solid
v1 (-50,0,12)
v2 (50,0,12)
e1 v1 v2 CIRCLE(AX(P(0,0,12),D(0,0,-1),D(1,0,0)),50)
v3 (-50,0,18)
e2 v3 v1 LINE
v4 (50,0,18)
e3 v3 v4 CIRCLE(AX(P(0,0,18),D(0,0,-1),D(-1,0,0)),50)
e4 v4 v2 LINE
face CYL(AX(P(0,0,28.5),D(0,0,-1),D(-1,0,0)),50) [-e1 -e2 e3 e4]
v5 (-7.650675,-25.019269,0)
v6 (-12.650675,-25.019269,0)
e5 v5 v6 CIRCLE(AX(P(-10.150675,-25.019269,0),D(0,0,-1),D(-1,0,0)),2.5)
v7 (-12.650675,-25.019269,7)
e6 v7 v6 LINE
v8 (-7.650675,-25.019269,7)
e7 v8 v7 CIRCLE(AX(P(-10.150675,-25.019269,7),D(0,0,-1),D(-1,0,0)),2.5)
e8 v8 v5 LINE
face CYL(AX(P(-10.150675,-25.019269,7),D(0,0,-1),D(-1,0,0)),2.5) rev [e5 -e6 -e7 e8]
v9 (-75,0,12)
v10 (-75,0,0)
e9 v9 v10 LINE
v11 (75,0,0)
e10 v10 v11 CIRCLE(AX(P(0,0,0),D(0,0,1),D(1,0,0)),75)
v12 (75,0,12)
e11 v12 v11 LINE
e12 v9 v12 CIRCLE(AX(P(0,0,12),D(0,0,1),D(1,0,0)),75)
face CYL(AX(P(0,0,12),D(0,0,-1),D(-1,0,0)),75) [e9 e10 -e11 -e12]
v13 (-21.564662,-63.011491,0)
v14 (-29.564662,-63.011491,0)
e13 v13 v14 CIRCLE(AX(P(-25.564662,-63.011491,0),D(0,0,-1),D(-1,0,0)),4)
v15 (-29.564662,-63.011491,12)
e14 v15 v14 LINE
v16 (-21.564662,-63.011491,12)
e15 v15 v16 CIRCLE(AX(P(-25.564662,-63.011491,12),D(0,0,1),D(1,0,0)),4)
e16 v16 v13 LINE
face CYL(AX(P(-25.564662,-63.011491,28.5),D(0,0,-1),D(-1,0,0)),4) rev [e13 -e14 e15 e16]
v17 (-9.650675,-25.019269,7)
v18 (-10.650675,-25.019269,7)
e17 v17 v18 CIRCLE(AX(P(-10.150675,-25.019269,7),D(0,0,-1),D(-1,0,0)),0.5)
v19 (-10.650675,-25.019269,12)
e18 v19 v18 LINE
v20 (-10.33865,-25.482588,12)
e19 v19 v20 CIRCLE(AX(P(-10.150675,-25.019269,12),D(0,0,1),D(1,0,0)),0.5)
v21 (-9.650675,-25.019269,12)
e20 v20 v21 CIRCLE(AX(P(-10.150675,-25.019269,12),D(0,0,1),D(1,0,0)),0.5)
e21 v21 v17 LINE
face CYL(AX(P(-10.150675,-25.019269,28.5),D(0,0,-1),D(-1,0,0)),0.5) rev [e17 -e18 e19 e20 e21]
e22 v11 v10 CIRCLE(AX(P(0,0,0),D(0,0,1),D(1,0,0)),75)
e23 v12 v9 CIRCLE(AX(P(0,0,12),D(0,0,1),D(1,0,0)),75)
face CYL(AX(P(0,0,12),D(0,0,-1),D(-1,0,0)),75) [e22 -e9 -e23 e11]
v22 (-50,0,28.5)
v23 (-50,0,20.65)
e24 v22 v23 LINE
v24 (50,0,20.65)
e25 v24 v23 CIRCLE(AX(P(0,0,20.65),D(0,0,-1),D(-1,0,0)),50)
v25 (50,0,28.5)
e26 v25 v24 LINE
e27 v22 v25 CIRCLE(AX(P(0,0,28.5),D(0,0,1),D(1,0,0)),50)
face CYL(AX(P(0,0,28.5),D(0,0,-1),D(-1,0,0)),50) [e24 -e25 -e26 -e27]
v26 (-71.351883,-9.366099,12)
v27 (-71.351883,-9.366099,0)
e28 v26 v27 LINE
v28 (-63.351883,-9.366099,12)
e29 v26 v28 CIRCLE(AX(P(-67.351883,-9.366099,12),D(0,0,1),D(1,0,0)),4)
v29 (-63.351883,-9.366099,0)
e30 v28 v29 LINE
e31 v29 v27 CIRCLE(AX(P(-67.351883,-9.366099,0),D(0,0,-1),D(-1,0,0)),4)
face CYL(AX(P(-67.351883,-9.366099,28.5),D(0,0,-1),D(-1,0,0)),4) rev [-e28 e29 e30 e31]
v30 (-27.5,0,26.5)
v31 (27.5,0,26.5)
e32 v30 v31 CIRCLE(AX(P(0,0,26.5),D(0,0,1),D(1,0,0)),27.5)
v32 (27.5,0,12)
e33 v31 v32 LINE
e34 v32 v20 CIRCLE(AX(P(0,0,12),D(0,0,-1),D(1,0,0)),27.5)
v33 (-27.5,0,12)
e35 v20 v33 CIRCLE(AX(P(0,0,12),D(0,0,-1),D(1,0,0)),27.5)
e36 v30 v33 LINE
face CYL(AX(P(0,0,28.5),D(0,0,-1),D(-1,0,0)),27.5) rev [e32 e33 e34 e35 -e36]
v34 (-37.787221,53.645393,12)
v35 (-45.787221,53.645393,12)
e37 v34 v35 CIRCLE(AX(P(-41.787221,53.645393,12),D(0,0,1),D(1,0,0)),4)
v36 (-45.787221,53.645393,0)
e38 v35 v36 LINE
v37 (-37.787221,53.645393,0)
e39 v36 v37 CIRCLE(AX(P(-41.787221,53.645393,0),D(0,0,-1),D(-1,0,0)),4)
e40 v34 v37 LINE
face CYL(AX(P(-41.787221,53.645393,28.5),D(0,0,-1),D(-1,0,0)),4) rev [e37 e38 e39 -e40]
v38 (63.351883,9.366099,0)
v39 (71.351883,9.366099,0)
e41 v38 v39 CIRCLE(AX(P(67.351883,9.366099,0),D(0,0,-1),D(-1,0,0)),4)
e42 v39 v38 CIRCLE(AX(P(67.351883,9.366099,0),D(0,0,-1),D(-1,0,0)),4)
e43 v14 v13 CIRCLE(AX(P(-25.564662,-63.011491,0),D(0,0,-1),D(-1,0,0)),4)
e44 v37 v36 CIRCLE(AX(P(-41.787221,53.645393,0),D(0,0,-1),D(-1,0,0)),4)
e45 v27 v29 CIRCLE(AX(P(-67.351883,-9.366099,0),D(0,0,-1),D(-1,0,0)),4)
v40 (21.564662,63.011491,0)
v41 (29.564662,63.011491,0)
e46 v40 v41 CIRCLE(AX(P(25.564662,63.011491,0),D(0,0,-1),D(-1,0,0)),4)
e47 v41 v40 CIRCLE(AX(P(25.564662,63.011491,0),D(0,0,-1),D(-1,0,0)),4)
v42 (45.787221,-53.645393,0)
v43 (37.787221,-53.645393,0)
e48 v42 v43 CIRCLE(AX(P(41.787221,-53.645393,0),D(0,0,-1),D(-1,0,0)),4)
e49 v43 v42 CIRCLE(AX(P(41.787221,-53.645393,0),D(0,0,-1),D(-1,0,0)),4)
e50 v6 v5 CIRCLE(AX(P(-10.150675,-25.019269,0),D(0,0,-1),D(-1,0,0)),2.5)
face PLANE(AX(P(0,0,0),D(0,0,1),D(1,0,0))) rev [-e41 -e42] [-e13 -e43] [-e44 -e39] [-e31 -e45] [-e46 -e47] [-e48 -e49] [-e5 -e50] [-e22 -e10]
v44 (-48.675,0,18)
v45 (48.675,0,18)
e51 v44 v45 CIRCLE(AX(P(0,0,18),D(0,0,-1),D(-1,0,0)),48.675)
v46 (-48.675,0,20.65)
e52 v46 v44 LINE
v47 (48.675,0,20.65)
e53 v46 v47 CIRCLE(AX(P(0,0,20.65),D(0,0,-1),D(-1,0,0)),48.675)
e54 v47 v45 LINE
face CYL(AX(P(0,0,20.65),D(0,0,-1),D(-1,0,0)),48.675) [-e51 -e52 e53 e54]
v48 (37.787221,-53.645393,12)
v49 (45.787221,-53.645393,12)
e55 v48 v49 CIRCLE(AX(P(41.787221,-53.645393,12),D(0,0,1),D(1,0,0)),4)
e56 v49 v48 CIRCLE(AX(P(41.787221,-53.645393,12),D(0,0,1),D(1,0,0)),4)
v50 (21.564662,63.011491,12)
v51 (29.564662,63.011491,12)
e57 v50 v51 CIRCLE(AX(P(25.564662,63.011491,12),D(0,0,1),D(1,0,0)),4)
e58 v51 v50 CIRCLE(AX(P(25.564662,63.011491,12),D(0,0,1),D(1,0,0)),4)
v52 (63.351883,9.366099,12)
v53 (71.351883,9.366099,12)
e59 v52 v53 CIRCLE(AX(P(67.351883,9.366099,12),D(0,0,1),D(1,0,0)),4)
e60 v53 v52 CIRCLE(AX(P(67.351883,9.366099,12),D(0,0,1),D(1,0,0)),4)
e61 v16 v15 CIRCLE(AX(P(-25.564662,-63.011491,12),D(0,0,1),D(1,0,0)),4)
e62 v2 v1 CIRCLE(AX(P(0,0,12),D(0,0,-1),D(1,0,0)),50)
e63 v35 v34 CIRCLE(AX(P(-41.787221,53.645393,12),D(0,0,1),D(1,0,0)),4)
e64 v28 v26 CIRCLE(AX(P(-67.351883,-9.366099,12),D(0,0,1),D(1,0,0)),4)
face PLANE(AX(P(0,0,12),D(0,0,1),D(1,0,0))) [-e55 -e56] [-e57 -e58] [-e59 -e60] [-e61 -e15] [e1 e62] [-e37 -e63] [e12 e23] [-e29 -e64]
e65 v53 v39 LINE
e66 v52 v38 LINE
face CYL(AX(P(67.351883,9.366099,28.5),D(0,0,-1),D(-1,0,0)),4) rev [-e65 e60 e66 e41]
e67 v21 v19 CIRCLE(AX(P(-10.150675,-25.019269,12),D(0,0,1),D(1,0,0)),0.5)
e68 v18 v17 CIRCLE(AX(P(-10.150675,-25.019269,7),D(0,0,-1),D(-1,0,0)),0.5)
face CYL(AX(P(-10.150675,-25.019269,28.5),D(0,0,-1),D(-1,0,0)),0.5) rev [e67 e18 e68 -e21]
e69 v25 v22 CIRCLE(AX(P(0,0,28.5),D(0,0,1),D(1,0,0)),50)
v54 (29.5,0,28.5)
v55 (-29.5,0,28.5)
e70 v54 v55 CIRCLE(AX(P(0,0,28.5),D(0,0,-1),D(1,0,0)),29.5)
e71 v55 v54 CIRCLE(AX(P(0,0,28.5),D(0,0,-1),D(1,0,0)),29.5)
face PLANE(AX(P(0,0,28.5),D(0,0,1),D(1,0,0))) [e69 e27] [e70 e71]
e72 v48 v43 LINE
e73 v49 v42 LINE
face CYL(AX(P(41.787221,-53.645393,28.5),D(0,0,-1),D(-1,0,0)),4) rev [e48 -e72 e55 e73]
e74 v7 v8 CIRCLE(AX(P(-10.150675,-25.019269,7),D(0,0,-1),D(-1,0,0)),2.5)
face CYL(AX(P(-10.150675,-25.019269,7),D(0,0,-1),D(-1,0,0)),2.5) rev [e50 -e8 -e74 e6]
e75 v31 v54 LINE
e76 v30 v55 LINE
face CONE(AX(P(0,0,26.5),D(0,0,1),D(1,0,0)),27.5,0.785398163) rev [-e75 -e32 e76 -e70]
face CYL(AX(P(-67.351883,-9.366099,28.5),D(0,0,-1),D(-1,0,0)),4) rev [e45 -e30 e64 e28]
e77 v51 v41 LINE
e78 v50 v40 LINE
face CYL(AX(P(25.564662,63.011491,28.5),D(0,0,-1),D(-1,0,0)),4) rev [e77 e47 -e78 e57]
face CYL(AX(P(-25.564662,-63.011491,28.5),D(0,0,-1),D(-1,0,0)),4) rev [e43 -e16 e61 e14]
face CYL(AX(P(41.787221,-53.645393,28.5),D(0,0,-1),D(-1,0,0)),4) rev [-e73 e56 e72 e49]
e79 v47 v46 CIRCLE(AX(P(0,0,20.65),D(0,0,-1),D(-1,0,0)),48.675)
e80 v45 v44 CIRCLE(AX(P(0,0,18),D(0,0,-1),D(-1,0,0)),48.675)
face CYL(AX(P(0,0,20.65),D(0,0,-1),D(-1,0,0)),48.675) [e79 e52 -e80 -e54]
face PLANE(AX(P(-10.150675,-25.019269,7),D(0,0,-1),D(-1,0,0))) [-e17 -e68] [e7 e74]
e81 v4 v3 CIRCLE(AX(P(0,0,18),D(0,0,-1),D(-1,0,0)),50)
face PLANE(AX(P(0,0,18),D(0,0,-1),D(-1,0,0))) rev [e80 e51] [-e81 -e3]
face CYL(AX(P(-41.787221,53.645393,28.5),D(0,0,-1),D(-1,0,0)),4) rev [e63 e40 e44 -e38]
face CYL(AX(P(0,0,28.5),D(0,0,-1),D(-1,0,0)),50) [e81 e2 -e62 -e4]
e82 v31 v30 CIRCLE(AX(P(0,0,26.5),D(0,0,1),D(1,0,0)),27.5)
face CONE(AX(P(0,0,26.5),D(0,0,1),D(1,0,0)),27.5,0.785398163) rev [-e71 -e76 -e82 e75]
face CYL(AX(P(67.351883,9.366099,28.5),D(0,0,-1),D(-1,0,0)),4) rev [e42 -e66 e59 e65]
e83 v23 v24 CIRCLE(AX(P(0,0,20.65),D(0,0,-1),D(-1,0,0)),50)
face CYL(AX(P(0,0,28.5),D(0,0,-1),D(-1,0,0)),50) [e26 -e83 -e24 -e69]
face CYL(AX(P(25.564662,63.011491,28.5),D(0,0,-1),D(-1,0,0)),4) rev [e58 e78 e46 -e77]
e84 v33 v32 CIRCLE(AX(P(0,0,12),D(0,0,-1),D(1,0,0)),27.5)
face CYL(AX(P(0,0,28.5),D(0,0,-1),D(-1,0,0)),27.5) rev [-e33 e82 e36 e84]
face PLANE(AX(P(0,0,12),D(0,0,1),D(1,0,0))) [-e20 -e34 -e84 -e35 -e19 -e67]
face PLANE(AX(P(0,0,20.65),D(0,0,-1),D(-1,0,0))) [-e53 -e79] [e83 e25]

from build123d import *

# Parameters (mm, degrees)
SKETCH1_R           = 75
BOSS_EXTRUDE1_DEPTH = 12
SKETCH2_R           = 50
SKETCH2_R_2         = 27.5
BOSS_EXTRUDE2_DEPTH = 28.5
CUT_EXTRUDE1_START  = -18
SKETCH3_R           = 50
SKETCH3_R_2         = 48.675
CUT_EXTRUDE1_DEPTH  = 2.65
CHAMFER1_SIZE       = 2
SKETCH7_R           = 4
CUT_EXTRUDE2_DEPTH  = 110.828275048
SKETCH10_R          = 2.5
CUT_EXTRUDE3_DEPTH  = 7
SKETCH12_R          = 0.5
CUT_EXTRUDE8_DEPTH  = 109.223149095


with BuildPart() as part:
    # Sketch1 → Boss-Extrude1 (new body)
    with BuildSketch(Plane.XY):
        Circle(SKETCH1_R)
    extrude(amount=BOSS_EXTRUDE1_DEPTH)

    # Sketch2 → Boss-Extrude2 (add)
    with BuildSketch(Plane.XY):
        with Locations(Location((0, 0, 0), (0, 0, 180))):
            Circle(SKETCH2_R)
        with Locations(Location((0, 0, 0), (0, 0, 180))):
            Circle(SKETCH2_R_2, mode=Mode.SUBTRACT)
    extrude(amount=BOSS_EXTRUDE2_DEPTH)

    # Sketch3 → Cut-Extrude1 (cut)
    with BuildSketch(Plane(origin=(0, 0, 0), x_dir=(-1, 0, 0), z_dir=(0, 0, -1)).offset(CUT_EXTRUDE1_START)):
        Circle(SKETCH3_R)
        Circle(SKETCH3_R_2, mode=Mode.SUBTRACT)
    extrude(amount=-CUT_EXTRUDE1_DEPTH, mode=Mode.SUBTRACT)

    # Chamfer1
    chamfer1_edges = [part.edges().sort_by_distance(p)[0] for p in [
        (27.5, 0, 28.5),
    ]]
    chamfer(chamfer1_edges, length=CHAMFER1_SIZE)

    # Sketch7 → Cut-Extrude2 (cut, through all)
    with BuildSketch(Plane(origin=(0, 0, 0), x_dir=(-1, 0, 0), z_dir=(0, 0, -1))):
        with Locations((-25.564662216, 63.011491379)):
            Circle(SKETCH7_R)
        with Locations((41.787221156, 53.645392608)):
            Circle(SKETCH7_R)
        with Locations((67.351883372, -9.366098771)):
            Circle(SKETCH7_R)
        with Locations((25.564662216, -63.011491379)):
            Circle(SKETCH7_R)
        with Locations((-41.787221156, -53.645392608)):
            Circle(SKETCH7_R)
        with Locations((-67.351883372, 9.366098771)):
            Circle(SKETCH7_R)
    extrude(amount=-CUT_EXTRUDE2_DEPTH, mode=Mode.SUBTRACT)

    # Sketch10 → Cut-Extrude3 (cut)
    with BuildSketch(Plane(origin=(0, 0, 0), x_dir=(-1, 0, 0), z_dir=(0, 0, -1))):
        with Locations((10.150674704, -25.019268636)):
            Circle(SKETCH10_R)
    extrude(amount=-CUT_EXTRUDE3_DEPTH, mode=Mode.SUBTRACT)

    # Sketch12 → Cut-Extrude8 (cut, through all)
    with BuildSketch(Plane(origin=(0, 0, 7), x_dir=(-1, 0, 0), z_dir=(0, 0, -1))):
        with Locations((10.150674704, -25.019268636)):
            Circle(SKETCH12_R)
    extrude(amount=-CUT_EXTRUDE8_DEPTH, mode=Mode.SUBTRACT)


solid = part.part
